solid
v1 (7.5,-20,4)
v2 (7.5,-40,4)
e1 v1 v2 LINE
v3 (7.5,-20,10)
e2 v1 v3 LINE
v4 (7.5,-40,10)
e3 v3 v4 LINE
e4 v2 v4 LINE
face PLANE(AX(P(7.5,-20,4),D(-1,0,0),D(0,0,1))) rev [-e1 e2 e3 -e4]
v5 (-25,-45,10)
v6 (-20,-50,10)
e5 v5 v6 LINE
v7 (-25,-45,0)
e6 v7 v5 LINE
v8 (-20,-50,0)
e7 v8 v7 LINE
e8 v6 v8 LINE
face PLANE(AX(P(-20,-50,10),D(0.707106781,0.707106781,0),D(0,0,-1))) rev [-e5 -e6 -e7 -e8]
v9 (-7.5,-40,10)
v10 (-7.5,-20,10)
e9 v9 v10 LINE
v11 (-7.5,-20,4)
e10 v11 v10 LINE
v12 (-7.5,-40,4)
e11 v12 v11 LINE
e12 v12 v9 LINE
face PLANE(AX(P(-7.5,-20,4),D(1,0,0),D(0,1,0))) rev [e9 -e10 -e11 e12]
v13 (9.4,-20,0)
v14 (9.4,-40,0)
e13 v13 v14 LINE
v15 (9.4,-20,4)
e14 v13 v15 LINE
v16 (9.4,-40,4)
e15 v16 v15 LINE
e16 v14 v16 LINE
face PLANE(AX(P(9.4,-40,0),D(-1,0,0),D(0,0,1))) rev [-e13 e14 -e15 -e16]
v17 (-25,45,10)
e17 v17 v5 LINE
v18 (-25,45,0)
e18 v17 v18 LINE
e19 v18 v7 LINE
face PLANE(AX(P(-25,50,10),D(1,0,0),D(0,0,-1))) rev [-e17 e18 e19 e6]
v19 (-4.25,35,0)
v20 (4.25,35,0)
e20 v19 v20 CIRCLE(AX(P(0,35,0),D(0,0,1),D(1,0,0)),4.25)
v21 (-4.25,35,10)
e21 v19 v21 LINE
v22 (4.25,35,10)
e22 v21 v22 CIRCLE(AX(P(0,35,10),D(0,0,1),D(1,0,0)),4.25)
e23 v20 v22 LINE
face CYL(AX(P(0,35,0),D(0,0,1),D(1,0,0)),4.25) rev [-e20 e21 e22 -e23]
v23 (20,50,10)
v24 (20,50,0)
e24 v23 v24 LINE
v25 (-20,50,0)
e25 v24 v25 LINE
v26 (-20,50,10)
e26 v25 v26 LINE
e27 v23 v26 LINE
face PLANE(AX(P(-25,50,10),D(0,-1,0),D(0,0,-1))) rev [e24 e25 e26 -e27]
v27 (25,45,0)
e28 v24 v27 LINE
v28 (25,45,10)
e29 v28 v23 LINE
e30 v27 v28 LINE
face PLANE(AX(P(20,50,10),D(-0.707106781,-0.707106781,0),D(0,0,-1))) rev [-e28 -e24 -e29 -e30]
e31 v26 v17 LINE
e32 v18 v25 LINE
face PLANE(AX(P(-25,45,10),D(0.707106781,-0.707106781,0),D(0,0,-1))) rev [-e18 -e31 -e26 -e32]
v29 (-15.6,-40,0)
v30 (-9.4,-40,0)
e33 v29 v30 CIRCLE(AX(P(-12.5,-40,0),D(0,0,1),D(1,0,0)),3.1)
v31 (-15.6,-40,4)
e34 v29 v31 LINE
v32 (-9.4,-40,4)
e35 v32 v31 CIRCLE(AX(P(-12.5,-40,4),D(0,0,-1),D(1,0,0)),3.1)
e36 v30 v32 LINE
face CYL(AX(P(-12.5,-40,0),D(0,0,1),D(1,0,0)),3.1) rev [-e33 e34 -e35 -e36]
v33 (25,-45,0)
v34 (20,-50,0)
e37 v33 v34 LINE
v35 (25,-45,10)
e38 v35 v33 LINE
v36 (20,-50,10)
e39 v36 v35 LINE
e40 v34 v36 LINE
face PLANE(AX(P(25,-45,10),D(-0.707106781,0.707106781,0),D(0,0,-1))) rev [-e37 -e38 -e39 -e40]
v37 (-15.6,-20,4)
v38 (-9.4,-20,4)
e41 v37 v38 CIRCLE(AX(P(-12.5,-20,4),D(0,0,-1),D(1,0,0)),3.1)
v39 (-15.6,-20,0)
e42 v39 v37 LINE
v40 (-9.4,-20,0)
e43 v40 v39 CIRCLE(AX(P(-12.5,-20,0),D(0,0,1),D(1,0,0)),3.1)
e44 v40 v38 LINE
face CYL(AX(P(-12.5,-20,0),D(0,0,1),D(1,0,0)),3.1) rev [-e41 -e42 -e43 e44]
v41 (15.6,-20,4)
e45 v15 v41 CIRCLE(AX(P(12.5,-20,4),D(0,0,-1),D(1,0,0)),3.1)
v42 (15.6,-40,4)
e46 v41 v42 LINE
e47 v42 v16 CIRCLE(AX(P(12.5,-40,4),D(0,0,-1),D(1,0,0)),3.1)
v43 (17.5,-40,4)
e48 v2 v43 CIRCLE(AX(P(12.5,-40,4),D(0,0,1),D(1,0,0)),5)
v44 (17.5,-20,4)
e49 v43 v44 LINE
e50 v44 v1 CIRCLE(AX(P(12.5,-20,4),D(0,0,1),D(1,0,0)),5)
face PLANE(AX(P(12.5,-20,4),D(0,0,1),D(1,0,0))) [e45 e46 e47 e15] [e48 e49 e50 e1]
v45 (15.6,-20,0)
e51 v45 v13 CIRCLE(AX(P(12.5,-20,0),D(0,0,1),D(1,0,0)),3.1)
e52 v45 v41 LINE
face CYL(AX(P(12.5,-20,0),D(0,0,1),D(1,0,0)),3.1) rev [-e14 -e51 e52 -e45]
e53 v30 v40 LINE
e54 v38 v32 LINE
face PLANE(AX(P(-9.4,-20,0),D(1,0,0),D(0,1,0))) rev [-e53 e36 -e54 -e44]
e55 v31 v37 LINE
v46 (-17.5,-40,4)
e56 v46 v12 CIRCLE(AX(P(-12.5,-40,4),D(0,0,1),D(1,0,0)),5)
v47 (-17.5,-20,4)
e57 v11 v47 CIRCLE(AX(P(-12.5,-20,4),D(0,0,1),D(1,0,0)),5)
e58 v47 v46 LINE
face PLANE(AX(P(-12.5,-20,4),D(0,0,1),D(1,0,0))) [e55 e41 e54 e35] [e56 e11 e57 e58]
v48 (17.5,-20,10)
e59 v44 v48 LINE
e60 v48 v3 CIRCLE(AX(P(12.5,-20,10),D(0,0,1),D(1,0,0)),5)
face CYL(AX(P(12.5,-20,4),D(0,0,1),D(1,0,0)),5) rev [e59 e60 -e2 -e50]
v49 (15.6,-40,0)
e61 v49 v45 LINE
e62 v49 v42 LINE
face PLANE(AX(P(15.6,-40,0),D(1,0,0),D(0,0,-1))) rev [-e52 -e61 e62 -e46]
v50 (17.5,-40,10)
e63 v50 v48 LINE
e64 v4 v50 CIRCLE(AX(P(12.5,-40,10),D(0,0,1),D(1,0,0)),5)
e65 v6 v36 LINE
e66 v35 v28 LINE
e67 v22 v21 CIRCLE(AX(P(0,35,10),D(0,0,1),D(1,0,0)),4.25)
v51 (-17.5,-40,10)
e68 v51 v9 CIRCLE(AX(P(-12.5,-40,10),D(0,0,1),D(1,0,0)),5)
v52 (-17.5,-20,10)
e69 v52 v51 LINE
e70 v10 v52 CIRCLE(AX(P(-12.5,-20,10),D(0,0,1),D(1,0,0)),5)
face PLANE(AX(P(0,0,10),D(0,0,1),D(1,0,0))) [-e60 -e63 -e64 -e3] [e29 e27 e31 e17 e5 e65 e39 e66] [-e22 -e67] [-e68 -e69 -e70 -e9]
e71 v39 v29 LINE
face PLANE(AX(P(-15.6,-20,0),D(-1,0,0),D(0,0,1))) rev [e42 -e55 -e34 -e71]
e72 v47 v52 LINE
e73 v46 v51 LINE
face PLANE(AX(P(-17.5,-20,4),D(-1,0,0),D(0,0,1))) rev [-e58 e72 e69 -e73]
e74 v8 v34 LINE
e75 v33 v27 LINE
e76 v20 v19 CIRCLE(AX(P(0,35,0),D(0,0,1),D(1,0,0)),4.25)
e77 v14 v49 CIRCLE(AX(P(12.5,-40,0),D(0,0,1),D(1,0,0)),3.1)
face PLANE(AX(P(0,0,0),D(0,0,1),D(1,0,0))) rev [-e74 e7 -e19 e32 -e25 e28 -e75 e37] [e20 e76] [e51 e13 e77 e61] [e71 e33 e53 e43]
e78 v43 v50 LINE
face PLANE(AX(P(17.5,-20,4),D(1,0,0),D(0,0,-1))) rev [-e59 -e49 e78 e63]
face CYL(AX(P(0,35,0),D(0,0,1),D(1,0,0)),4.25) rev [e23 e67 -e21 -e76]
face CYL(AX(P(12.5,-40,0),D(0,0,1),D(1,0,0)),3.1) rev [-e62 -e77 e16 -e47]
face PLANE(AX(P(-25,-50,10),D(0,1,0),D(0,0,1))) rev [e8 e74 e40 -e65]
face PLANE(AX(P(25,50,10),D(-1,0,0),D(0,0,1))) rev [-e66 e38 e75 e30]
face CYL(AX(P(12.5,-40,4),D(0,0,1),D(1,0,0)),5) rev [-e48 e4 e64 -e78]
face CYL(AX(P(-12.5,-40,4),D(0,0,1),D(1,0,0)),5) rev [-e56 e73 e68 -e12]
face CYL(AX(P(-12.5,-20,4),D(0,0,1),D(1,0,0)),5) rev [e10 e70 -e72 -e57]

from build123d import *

# Parameters (mm, degrees)
SKETCH_1_W          = 50
SKETCH_1_H          = 100
EXTRUDE_1_DEPTH     = 10
CUT_EXTRUDE_1_DEPTH = 10
CUT_EXTRUDE_2_DEPTH = 6
CHAMFER_1_SIZE      = 5
SKETCH_4_R          = 4.25
CUT_EXTRUDE_3_DEPTH = 10


with BuildPart() as part:
    # 草图1 → 凸台-拉伸1 (new body)
    with BuildSketch(Plane.XY):
        Rectangle(SKETCH_1_W, SKETCH_1_H)
    extrude(amount=EXTRUDE_1_DEPTH)

    # 草图2 → 切除-拉伸1 (cut)
    with BuildSketch(Plane.XY.offset(10)):
        with BuildLine():
            Line((-9.4, -20), (-9.4, -40))
            ThreePointArc((-9.4, -40), (-12.5, -43.1), (-15.6, -40))
            Line((-15.6, -40), (-15.6, -20))
            ThreePointArc((-15.6, -20), (-12.5, -16.9), (-9.4, -20))
        make_face()
        with BuildLine():
            Line((9.4, -40), (9.4, -20))
            ThreePointArc((9.4, -20), (12.5, -16.9), (15.6, -20))
            Line((15.6, -20), (15.6, -40))
            ThreePointArc((15.6, -40), (12.5, -43.1), (9.4, -40))
        make_face()
    extrude(amount=-CUT_EXTRUDE_1_DEPTH, mode=Mode.SUBTRACT)

    # 草图3 → 切除-拉伸2 (cut)
    with BuildSketch(Plane.XY.offset(10)):
        with BuildLine():
            Line((-7.5, -20), (-7.5, -40))
            ThreePointArc((-7.5, -40), (-12.5, -45), (-17.5, -40))
            Line((-17.5, -40), (-17.5, -20))
            ThreePointArc((-17.5, -20), (-12.5, -15), (-7.5, -20))
        make_face()
        with BuildLine():
            Line((17.5, -20), (17.5, -40))
            ThreePointArc((17.5, -40), (12.5, -45), (7.5, -40))
            Line((7.5, -40), (7.5, -20))
            ThreePointArc((7.5, -20), (12.5, -15), (17.5, -20))
        make_face()
    extrude(amount=-CUT_EXTRUDE_2_DEPTH, mode=Mode.SUBTRACT)

    # 倒角1
    chamfer_1_edges = [part.edges().sort_by_distance(p)[0] for p in [
        (25, -50, 5),
        (-25, -50, 5),
        (-25, 50, 5),
        (25, 50, 5),
    ]]
    chamfer(chamfer_1_edges, length=CHAMFER_1_SIZE)

    # 草图4 → 切除-拉伸3 (cut)
    with BuildSketch(Plane.XY.offset(10)):
        with Locations((0, 35)):
            Circle(SKETCH_4_R)
    extrude(amount=-CUT_EXTRUDE_3_DEPTH, mode=Mode.SUBTRACT)


solid = part.part
